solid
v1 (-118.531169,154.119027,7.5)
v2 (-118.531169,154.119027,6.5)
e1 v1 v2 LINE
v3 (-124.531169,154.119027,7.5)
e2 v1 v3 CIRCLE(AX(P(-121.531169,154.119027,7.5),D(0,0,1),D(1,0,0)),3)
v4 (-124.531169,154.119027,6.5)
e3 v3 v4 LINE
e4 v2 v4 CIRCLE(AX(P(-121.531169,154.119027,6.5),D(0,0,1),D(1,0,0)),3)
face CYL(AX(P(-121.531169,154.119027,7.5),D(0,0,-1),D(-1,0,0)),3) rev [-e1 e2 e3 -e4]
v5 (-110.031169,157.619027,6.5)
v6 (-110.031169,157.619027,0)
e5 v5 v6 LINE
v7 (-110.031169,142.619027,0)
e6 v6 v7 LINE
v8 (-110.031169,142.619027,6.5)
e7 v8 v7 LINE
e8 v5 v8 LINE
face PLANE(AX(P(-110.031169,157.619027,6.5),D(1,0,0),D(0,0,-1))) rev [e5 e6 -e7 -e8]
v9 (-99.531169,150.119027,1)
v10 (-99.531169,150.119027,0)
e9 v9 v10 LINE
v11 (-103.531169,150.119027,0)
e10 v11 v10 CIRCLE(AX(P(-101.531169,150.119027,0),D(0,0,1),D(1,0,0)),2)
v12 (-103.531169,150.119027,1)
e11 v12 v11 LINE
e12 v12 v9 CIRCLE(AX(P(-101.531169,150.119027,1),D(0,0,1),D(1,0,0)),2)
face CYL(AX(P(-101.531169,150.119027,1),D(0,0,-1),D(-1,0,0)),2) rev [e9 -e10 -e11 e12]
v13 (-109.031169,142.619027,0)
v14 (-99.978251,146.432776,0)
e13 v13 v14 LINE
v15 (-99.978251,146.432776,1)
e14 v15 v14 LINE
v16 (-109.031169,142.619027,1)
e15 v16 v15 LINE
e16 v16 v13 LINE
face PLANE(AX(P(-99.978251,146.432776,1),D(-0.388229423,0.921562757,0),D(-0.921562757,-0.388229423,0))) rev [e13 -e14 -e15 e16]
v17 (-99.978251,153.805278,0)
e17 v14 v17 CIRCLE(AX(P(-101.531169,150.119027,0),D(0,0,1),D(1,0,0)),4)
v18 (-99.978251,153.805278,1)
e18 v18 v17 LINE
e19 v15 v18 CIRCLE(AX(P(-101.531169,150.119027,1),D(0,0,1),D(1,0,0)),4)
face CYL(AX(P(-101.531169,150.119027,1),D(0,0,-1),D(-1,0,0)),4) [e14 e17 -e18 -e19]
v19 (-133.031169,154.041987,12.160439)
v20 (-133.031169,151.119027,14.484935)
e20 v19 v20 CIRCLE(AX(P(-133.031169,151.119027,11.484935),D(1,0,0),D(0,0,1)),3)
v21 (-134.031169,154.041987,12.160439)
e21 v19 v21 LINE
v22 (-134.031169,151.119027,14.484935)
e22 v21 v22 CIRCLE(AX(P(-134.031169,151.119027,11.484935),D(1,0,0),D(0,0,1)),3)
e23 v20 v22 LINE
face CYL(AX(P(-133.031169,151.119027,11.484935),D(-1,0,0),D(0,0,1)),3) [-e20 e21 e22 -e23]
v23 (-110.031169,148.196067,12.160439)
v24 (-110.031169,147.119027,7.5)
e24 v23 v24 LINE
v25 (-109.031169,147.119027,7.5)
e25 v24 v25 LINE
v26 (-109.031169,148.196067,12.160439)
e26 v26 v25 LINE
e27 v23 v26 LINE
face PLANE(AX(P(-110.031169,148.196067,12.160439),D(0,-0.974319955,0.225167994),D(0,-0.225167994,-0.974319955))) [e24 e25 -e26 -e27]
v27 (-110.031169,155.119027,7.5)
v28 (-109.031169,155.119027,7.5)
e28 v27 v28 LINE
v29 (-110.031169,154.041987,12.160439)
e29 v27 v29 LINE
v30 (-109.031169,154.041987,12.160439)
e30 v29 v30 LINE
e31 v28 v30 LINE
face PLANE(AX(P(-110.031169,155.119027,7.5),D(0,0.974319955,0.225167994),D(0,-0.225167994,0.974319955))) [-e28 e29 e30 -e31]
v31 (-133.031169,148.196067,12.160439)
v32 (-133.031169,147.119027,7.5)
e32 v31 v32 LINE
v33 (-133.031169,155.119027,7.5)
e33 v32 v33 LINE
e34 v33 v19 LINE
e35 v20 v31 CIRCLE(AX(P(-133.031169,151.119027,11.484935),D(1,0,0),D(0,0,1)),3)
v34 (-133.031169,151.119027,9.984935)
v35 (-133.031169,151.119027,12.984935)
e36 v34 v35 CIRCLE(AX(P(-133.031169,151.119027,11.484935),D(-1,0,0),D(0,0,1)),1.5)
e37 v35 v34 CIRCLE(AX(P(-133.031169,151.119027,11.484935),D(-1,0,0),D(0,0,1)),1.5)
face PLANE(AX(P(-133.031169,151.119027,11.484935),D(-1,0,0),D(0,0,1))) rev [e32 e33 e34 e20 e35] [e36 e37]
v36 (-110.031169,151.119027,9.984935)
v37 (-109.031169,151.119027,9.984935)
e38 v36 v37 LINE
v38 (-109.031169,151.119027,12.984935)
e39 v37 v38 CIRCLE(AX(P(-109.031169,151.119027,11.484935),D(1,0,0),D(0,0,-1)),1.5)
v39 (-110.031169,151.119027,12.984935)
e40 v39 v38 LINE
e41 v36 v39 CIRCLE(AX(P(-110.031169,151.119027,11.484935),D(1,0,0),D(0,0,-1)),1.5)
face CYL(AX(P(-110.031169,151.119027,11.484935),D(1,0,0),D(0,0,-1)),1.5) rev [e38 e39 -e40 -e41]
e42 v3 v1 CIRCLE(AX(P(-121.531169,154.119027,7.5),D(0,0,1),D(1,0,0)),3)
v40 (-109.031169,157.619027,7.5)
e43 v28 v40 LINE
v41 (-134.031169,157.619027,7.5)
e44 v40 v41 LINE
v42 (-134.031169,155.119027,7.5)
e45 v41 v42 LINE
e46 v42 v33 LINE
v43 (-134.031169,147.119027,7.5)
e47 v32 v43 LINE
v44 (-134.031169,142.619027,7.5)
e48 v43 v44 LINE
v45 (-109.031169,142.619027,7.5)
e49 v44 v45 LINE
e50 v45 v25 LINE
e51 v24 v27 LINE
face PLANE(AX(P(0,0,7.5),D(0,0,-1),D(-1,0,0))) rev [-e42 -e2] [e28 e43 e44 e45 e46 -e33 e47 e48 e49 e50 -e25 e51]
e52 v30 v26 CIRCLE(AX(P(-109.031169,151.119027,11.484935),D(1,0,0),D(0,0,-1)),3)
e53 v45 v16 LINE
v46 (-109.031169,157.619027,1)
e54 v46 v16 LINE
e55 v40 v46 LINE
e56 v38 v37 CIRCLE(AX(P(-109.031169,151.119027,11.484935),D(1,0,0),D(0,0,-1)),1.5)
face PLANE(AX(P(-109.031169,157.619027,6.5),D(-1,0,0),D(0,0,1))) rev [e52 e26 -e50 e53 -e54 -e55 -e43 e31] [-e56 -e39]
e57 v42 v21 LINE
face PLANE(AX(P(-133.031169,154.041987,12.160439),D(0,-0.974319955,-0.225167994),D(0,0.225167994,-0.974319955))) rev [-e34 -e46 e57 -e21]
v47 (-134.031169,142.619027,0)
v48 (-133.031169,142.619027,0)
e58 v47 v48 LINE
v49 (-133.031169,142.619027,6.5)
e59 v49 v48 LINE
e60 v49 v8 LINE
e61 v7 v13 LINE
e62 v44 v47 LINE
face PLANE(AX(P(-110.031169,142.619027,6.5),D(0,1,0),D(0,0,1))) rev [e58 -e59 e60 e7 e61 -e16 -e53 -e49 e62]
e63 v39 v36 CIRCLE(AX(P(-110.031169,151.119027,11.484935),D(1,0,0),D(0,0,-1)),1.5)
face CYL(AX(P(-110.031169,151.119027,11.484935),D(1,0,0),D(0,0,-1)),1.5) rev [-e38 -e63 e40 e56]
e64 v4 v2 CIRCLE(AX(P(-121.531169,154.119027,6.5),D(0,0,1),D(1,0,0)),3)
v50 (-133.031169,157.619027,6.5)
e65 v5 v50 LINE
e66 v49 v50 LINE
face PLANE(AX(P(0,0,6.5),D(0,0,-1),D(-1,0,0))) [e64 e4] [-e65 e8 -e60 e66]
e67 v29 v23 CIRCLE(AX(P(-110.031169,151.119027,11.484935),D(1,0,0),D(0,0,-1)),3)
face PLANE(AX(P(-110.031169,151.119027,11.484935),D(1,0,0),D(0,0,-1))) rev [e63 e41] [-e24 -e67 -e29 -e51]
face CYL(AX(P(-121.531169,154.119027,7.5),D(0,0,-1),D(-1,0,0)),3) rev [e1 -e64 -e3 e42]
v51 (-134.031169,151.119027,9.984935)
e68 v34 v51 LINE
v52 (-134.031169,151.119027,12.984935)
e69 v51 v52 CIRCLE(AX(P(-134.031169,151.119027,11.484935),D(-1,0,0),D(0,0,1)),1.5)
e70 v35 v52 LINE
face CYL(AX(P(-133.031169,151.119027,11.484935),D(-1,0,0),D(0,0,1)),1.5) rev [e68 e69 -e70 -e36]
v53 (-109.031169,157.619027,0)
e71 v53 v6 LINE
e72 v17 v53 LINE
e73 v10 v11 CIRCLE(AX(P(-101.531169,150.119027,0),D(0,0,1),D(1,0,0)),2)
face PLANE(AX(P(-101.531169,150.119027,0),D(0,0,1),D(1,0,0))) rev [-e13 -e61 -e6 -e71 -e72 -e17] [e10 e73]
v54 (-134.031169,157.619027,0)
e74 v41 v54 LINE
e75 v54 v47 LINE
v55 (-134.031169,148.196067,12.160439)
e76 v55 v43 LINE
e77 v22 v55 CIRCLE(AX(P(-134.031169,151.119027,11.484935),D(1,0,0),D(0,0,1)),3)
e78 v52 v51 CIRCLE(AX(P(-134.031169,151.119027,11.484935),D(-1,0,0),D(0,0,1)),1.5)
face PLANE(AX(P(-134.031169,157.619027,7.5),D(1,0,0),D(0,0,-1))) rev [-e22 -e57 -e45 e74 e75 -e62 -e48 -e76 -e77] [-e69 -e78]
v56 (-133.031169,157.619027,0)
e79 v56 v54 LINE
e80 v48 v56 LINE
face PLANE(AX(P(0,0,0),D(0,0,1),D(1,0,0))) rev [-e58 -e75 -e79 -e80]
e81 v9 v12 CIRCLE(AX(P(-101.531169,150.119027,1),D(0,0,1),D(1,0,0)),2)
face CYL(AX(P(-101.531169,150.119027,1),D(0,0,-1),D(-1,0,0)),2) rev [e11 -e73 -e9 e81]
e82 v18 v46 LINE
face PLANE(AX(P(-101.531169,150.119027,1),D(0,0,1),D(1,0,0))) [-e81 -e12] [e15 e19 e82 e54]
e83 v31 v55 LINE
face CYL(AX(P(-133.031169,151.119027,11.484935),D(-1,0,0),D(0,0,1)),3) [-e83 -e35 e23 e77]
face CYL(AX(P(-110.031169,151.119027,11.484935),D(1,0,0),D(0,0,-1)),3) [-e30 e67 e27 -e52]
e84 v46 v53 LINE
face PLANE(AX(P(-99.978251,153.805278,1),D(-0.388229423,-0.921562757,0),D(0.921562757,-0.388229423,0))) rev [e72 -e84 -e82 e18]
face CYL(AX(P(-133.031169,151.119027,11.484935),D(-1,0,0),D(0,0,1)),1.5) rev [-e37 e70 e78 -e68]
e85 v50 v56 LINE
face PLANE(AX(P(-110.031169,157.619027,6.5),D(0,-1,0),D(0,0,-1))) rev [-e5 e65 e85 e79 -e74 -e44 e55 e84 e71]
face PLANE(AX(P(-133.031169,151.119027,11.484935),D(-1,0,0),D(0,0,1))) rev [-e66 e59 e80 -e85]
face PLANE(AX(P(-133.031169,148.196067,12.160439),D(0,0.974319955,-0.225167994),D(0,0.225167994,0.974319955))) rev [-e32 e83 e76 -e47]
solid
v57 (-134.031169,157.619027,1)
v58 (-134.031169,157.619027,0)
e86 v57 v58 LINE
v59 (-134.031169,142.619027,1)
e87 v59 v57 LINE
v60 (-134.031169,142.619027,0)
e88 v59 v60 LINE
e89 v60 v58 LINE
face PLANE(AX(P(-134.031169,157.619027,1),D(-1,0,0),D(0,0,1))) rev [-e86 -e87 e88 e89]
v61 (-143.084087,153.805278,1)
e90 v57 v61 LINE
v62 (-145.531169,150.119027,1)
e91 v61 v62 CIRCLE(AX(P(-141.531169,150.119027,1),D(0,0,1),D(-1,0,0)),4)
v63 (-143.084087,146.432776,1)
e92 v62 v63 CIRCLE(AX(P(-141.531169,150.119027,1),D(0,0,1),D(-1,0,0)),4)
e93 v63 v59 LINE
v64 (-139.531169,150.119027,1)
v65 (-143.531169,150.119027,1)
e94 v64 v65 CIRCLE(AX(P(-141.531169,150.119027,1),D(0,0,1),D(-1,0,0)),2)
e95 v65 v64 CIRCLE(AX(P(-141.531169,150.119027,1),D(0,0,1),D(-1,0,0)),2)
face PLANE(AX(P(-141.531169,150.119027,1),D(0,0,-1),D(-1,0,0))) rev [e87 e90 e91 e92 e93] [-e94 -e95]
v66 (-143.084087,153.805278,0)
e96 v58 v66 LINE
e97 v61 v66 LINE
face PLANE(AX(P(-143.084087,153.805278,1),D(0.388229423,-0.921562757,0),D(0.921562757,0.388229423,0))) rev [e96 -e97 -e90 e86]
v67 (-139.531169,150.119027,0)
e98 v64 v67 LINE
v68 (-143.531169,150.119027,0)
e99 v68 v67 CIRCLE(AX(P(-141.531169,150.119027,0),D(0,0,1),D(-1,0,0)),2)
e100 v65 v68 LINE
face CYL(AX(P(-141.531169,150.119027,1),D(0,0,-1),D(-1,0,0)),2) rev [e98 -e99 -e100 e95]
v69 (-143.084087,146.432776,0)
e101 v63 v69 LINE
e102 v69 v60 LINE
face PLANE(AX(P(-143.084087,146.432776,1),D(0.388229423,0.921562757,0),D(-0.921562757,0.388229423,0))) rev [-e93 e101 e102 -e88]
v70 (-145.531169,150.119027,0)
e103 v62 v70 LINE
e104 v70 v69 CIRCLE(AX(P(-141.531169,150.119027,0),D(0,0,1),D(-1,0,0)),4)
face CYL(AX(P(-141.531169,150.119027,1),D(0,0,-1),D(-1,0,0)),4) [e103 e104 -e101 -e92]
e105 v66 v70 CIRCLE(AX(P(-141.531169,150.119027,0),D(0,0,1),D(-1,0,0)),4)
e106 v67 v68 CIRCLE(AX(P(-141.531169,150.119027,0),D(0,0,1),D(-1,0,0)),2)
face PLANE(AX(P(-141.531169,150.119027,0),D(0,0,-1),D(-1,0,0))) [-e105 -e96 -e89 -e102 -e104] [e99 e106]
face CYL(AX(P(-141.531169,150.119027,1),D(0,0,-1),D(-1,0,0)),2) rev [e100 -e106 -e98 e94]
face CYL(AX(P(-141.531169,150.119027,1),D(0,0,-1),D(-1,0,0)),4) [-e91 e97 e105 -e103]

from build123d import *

# Parameters (mm, degrees)
SKETCH1_R             = 2
BOSS_EXTRUDE1_DEPTH   = 1
BOSS_EXTRUDE1_2_DEPTH = 1
SKETCH2_W             = 1
SKETCH2_H             = 15
BOSS_EXTRUDE2_DEPTH   = 6.5
SKETCH4_W             = 24.99999999
SKETCH4_H             = 15
SKETCH4_R             = 3
BOSS_EXTRUDE3_DEPTH   = 1
SKETCH6_R             = 1.5
BOSS_EXTRUDE4_DEPTH   = 1
CUT_EXTRUDE1_DEPTH    = 1
SKETCH8_R             = 1.5
BOSS_EXTRUDE5_DEPTH   = 1


with BuildPart() as part:
    # Sketch1 → Boss-Extrude1 (new body)
    with BuildSketch(Plane.XY):
        with BuildLine():
            Line((-99.978251459, 146.432775889), (-109.031169153, 142.619026916))
            Line((-109.031169153, 142.619026916), (-109.031169153, 157.619026916))
            Line((-109.031169153, 157.619026916), (-99.978251459, 153.805277943))
            ThreePointArc((-99.978251459, 153.805277943), (-97.531169153, 150.119026916), (-99.978251459, 146.432775889))
        make_face()
        with Locations((-101.531169153, 150.119026916)):
            Circle(SKETCH1_R, mode=Mode.SUBTRACT)
    extrude(amount=BOSS_EXTRUDE1_DEPTH)

    # Sketch2 → Boss-Extrude2 (add)
    with BuildSketch(Plane.XY):
        with Locations((-109.531169153, 150.119026916)):
            Rectangle(SKETCH2_W, SKETCH2_H)
        with Locations((-133.531169143, 150.119026916)):
            Rectangle(SKETCH2_W, SKETCH2_H)
    extrude(amount=BOSS_EXTRUDE2_DEPTH)


with BuildPart() as body_2:
    # Sketch1 → Boss-Extrude1 2 (new body)
    with BuildSketch(Plane.XY):
        with BuildLine():
            Line((-143.084086847, 153.805277943), (-134.031169153, 157.619026916))
            Line((-134.031169153, 157.619026916), (-134.031169153, 142.619026916))
            Line((-134.031169153, 142.619026916), (-143.084086847, 146.432775889))
            ThreePointArc((-143.084086847, 146.432775889), (-145.531169153, 150.119026916), (-143.084086847, 153.805277943))
        make_face()
        with Locations(Location((-141.531169153, 150.119026916, 0), (0, 0, 180))):
            Circle(SKETCH1_R, mode=Mode.SUBTRACT)
    extrude(amount=BOSS_EXTRUDE1_2_DEPTH)


with BuildPart() as boss_extrude2_piece_1:
    # of the separate pieces the step leaves, piece 1, a body of its own (boss_extrude2_pieces)
    add(part.part.solids().sort_by_distance((-99.978251459, 146.432775889, 0))[0])

    # Sketch4 → Boss-Extrude3 (add)
    with BuildSketch(Plane.XY.offset(6.5)):
        with Locations((-121.531169148, 150.119026916)):
            Rectangle(SKETCH4_W, SKETCH4_H)
        with Locations((-121.531169153, 154.119026916)):
            Circle(SKETCH4_R, mode=Mode.SUBTRACT)
    extrude(amount=BOSS_EXTRUDE3_DEPTH)



with BuildPart() as boss_extrude2_piece_2:
    # of the separate pieces the step leaves, piece 2, a body of its own (boss_extrude2_pieces)
    add(part.part.solids().sort_by_distance((-134.031169143, 157.619026916, 0))[0])


with BuildPart() as boss_extrude2_piece_1_1:
    add(boss_extrude2_piece_1.part)

    add(boss_extrude2_piece_2.part)  # Boss-Extrude4 merges Boss-Extrude2 piece 2
    # Sketch6 → Boss-Extrude4 (add)
    with BuildSketch(Plane.ZY.offset(134.031169143)):
        with BuildLine():
            Line((11.484935003, 147.119026916), (5.675712497, 147.119026916))
            ThreePointArc((5.675712497, 147.119026916), (1.675712497, 151.119026916), (5.675712497, 155.119026916))
            Line((5.675712497, 155.119026916), (11.484935003, 155.119026916))
            ThreePointArc((11.484935003, 155.119026916), (15.484935003, 151.119026916), (11.484935003, 147.119026916))
        make_face()
        with Locations((11.484935003, 151.119026916)):
            Circle(SKETCH6_R, mode=Mode.SUBTRACT)
    extrude(amount=-BOSS_EXTRUDE4_DEPTH)

    # Sketch7 → Cut-Extrude1 (cut)
    with BuildSketch(Plane.ZY.offset(134.031169143)):
        with BuildLine():
            Line((12.160438985, 154.041986781), (7.5, 155.119026916))
            Line((7.5, 155.119026916), (10.709914087, 160.89800408))
            Line((10.709914087, 160.89800408), (15.340416768, 156.67870434))
            Line((15.340416768, 156.67870434), (15.715862932, 151.386701277))
            Line((15.715862932, 151.386701277), (14.535889275, 146.058941435))
            Line((14.535889275, 146.058941435), (7.5, 147.119026916))
            Line((7.5, 147.119026916), (12.160438985, 148.196067051))
            ThreePointArc((12.160438985, 148.196067051), (14.484935003, 151.119026916), (12.160438985, 154.041986781))
        make_face()
    extrude(amount=-CUT_EXTRUDE1_DEPTH, mode=Mode.SUBTRACT)

    # Sketch8 → Boss-Extrude5 (add)
    with BuildSketch(Plane(origin=(-109.031169153, 0, 0), x_dir=(0, 0, -1), z_dir=(1, 0, 0))):
        with BuildLine():
            Line((-7.5, 147.119026916), (-7.5, 155.119026916))
            Line((-7.5, 155.119026916), (-12.160438985, 154.041986781))
            ThreePointArc((-12.160438985, 154.041986781), (-14.484935003, 151.119026916), (-12.160438985, 148.196067051))
            Line((-12.160438985, 148.196067051), (-7.5, 147.119026916))
        make_face()
        with Locations(Location((-11.484935003, 151.119026916, 0), (0, 0, 180))):
            Circle(SKETCH8_R, mode=Mode.SUBTRACT)
    extrude(amount=-BOSS_EXTRUDE5_DEPTH)


solid = Compound([body_2.part, boss_extrude2_piece_1_1.part])
